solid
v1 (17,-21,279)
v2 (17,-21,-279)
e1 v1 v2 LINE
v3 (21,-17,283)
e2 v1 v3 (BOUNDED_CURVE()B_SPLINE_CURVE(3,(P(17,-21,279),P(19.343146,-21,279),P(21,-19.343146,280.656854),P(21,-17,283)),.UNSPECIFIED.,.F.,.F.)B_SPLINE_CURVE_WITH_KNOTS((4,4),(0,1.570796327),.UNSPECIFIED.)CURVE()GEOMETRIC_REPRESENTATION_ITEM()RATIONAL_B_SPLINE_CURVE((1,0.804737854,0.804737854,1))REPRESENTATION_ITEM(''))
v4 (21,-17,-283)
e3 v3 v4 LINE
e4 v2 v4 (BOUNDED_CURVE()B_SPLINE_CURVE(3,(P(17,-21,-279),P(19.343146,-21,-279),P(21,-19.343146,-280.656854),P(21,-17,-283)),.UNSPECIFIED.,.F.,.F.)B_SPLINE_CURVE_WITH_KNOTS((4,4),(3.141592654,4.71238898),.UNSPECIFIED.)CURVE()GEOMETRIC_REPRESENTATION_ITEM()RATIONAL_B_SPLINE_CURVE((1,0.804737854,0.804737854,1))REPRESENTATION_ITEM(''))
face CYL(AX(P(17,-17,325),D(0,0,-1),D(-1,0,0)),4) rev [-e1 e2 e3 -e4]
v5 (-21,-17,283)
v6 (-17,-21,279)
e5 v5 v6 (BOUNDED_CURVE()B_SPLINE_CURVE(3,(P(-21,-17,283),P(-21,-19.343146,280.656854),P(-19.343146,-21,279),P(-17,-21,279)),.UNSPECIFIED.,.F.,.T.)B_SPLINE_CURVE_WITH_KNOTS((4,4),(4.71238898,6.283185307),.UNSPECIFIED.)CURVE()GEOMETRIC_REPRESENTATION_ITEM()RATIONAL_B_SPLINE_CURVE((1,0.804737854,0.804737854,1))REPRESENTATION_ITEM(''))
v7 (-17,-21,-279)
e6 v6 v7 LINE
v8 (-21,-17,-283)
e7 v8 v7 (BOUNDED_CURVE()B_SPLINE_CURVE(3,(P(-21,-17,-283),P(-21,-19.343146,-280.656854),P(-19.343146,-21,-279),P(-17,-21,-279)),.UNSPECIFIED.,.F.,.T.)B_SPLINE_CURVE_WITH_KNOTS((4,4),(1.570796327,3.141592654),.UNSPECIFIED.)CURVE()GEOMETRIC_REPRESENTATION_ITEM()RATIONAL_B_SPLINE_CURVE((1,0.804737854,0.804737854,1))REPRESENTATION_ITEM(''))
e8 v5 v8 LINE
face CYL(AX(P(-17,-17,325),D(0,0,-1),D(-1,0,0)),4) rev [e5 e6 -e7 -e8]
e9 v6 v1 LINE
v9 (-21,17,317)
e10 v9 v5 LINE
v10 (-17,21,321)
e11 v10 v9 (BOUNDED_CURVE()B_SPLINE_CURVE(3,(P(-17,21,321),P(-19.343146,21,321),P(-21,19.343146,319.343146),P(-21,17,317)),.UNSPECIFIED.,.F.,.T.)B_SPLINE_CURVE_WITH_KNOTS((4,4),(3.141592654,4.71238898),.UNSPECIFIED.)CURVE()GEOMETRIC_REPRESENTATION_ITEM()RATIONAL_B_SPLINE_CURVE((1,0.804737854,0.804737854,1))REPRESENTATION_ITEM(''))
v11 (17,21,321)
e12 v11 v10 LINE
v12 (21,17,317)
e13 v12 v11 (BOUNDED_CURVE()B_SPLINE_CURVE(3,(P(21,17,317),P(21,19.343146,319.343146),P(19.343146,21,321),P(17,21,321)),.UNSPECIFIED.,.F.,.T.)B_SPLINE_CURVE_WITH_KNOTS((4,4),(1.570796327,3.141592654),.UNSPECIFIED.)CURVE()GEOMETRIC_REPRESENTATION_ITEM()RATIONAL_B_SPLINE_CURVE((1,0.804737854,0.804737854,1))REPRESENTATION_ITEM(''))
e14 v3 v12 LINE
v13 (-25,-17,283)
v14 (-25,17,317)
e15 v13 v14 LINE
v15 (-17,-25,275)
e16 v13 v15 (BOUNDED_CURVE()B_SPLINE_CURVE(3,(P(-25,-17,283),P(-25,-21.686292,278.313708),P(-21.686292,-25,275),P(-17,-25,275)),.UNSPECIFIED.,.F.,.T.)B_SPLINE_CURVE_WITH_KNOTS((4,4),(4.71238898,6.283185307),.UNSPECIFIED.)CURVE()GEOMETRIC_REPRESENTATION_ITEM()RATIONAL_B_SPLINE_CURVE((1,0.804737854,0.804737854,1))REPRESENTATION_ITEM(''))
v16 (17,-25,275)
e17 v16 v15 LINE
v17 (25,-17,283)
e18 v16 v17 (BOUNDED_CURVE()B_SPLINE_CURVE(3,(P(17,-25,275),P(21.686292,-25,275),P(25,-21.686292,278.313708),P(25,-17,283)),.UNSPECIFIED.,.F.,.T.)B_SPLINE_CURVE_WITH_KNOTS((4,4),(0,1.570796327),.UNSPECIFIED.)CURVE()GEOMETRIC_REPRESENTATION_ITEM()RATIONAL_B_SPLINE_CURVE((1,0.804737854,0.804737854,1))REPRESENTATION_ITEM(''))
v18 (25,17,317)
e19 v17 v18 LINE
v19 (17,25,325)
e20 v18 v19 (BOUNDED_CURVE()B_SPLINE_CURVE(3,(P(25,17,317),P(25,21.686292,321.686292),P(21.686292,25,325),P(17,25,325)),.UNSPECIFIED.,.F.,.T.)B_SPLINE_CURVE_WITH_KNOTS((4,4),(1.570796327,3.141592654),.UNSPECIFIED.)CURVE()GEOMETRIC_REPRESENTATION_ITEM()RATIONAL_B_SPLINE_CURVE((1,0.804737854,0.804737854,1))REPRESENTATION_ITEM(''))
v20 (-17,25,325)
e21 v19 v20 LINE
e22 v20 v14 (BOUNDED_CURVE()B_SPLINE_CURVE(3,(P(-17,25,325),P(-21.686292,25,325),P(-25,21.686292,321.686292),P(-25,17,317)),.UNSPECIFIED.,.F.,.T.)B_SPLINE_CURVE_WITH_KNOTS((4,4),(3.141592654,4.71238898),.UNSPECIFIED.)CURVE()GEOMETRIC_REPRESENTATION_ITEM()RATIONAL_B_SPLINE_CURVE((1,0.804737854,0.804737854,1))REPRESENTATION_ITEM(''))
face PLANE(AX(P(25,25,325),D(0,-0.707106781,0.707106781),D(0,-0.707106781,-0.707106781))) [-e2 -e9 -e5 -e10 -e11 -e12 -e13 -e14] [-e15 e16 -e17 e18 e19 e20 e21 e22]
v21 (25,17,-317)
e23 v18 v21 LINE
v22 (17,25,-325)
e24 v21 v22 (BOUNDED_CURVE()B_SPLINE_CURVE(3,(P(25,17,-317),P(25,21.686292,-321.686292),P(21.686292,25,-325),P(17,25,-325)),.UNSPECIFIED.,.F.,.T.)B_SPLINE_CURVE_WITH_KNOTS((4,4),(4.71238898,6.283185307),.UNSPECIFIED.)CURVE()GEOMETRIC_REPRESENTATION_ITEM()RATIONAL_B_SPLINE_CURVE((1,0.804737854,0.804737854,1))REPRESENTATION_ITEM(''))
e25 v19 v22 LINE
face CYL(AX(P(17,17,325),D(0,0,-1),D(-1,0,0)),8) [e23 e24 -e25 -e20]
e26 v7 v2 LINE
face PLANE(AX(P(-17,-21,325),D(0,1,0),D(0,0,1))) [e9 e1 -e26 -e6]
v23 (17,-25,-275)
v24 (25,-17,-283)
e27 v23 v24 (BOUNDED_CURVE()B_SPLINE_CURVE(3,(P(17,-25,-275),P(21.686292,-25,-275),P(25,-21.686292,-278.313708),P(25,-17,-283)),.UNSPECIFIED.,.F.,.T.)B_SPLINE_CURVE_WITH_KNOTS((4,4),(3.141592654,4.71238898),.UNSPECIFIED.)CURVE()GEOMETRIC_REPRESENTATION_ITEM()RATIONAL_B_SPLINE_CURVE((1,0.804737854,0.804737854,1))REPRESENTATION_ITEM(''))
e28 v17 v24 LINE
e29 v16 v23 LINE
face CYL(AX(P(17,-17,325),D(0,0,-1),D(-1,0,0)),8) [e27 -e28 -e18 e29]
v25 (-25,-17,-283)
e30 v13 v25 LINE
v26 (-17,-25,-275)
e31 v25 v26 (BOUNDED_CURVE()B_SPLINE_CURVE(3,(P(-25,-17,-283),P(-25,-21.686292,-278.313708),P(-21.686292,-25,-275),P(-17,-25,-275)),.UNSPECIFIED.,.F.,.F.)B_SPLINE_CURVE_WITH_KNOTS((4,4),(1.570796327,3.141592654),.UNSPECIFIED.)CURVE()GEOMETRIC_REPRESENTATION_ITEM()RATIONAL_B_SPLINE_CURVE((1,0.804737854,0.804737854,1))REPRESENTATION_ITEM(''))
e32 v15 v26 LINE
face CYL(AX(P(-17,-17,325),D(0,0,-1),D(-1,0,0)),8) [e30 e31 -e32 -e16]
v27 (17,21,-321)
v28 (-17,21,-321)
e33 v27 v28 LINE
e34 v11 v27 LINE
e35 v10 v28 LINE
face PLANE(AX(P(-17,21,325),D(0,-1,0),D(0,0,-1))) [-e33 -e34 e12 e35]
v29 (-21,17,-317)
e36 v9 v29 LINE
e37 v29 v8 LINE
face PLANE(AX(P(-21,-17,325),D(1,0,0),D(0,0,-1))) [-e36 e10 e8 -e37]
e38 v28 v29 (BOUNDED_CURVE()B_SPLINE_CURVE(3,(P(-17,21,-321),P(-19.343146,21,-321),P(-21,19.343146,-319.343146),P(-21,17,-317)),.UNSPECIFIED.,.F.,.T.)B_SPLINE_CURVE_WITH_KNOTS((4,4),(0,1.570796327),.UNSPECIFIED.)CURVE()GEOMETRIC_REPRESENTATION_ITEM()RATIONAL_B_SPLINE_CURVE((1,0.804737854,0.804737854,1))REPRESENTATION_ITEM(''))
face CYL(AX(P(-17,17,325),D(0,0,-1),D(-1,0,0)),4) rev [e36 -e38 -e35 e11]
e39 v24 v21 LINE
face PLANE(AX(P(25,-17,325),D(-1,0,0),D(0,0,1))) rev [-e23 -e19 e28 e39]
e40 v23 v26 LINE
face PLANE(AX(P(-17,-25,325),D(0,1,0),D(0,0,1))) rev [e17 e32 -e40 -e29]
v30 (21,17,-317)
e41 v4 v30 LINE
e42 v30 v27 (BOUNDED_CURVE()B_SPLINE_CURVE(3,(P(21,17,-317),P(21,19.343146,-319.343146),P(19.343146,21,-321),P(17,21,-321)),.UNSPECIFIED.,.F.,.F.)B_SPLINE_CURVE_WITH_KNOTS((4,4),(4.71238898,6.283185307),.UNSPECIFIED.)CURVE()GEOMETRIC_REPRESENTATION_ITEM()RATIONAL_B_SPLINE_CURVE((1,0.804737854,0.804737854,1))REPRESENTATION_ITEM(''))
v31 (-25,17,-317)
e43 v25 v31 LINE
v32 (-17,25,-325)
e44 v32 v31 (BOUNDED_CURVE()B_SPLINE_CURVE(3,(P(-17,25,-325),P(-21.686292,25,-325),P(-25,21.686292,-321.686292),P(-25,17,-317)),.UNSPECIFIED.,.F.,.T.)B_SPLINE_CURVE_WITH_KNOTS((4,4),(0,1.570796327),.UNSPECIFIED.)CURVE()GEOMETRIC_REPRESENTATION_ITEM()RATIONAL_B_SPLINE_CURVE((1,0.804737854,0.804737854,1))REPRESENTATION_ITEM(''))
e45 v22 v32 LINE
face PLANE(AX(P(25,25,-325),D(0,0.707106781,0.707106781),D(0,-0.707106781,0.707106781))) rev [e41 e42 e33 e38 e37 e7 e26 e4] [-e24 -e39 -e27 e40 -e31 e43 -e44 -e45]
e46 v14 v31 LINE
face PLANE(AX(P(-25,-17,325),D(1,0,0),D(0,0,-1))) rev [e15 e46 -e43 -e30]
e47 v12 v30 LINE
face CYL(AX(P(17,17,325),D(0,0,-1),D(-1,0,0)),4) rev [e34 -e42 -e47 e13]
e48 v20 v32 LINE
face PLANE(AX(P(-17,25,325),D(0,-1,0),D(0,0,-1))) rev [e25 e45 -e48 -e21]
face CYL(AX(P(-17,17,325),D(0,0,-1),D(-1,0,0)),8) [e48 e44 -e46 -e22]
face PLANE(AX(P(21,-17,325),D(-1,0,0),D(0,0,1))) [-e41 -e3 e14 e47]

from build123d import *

# Parameters (mm, degrees)
BOSS_EXTRUDE1_DEPTH = 325
CUT_EXTRUDE1_DEPTH  = 330.772648957


with BuildPart() as part:
    # Sketch1 → Boss-Extrude1 (new, symmetric)
    with BuildSketch(Plane.XY):
        with BuildLine():
            Line((-17, -25), (17, -25))
            ThreePointArc((17, -25), (22.656854249, -22.656854249), (25, -17))
            Line((25, -17), (25, 17))
            ThreePointArc((25, 17), (22.656854249, 22.656854249), (17, 25))
            Line((17, 25), (-17, 25))
            ThreePointArc((-17, 25), (-22.656854249, 22.656854249), (-25, 17))
            Line((-25, 17), (-25, -17))
            ThreePointArc((-25, -17), (-22.656854249, -22.656854249), (-17, -25))
        make_face()
        with BuildLine():
            Line((-17, 21), (17, 21))
            ThreePointArc((17, 21), (19.828427125, 19.828427125), (21, 17))
            Line((21, 17), (21, -17))
            ThreePointArc((21, -17), (19.828427125, -19.828427125), (17, -21))
            Line((17, -21), (-17, -21))
            ThreePointArc((-17, -21), (-19.828427125, -19.828427125), (-21, -17))
            Line((-21, -17), (-21, 17))
            ThreePointArc((-21, 17), (-19.828427125, 19.828427125), (-17, 21))
        make_face(mode=Mode.SUBTRACT)
    extrude(amount=BOSS_EXTRUDE1_DEPTH, both=True)

    # Sketch2 → Cut-Extrude1 (cut, through all)
    with BuildSketch(Plane.ZY.offset(25)):
        Polygon((-325, 25), (-275, -25), (-325, -25), align=None)
    cut_extrude1 = extrude(amount=-CUT_EXTRUDE1_DEPTH, mode=Mode.SUBTRACT)

    # Mirror1: Cut-Extrude1 across plane
    add(cut_extrude1.mirror(Plane.XY), mode=Mode.SUBTRACT)


solid = part.part
